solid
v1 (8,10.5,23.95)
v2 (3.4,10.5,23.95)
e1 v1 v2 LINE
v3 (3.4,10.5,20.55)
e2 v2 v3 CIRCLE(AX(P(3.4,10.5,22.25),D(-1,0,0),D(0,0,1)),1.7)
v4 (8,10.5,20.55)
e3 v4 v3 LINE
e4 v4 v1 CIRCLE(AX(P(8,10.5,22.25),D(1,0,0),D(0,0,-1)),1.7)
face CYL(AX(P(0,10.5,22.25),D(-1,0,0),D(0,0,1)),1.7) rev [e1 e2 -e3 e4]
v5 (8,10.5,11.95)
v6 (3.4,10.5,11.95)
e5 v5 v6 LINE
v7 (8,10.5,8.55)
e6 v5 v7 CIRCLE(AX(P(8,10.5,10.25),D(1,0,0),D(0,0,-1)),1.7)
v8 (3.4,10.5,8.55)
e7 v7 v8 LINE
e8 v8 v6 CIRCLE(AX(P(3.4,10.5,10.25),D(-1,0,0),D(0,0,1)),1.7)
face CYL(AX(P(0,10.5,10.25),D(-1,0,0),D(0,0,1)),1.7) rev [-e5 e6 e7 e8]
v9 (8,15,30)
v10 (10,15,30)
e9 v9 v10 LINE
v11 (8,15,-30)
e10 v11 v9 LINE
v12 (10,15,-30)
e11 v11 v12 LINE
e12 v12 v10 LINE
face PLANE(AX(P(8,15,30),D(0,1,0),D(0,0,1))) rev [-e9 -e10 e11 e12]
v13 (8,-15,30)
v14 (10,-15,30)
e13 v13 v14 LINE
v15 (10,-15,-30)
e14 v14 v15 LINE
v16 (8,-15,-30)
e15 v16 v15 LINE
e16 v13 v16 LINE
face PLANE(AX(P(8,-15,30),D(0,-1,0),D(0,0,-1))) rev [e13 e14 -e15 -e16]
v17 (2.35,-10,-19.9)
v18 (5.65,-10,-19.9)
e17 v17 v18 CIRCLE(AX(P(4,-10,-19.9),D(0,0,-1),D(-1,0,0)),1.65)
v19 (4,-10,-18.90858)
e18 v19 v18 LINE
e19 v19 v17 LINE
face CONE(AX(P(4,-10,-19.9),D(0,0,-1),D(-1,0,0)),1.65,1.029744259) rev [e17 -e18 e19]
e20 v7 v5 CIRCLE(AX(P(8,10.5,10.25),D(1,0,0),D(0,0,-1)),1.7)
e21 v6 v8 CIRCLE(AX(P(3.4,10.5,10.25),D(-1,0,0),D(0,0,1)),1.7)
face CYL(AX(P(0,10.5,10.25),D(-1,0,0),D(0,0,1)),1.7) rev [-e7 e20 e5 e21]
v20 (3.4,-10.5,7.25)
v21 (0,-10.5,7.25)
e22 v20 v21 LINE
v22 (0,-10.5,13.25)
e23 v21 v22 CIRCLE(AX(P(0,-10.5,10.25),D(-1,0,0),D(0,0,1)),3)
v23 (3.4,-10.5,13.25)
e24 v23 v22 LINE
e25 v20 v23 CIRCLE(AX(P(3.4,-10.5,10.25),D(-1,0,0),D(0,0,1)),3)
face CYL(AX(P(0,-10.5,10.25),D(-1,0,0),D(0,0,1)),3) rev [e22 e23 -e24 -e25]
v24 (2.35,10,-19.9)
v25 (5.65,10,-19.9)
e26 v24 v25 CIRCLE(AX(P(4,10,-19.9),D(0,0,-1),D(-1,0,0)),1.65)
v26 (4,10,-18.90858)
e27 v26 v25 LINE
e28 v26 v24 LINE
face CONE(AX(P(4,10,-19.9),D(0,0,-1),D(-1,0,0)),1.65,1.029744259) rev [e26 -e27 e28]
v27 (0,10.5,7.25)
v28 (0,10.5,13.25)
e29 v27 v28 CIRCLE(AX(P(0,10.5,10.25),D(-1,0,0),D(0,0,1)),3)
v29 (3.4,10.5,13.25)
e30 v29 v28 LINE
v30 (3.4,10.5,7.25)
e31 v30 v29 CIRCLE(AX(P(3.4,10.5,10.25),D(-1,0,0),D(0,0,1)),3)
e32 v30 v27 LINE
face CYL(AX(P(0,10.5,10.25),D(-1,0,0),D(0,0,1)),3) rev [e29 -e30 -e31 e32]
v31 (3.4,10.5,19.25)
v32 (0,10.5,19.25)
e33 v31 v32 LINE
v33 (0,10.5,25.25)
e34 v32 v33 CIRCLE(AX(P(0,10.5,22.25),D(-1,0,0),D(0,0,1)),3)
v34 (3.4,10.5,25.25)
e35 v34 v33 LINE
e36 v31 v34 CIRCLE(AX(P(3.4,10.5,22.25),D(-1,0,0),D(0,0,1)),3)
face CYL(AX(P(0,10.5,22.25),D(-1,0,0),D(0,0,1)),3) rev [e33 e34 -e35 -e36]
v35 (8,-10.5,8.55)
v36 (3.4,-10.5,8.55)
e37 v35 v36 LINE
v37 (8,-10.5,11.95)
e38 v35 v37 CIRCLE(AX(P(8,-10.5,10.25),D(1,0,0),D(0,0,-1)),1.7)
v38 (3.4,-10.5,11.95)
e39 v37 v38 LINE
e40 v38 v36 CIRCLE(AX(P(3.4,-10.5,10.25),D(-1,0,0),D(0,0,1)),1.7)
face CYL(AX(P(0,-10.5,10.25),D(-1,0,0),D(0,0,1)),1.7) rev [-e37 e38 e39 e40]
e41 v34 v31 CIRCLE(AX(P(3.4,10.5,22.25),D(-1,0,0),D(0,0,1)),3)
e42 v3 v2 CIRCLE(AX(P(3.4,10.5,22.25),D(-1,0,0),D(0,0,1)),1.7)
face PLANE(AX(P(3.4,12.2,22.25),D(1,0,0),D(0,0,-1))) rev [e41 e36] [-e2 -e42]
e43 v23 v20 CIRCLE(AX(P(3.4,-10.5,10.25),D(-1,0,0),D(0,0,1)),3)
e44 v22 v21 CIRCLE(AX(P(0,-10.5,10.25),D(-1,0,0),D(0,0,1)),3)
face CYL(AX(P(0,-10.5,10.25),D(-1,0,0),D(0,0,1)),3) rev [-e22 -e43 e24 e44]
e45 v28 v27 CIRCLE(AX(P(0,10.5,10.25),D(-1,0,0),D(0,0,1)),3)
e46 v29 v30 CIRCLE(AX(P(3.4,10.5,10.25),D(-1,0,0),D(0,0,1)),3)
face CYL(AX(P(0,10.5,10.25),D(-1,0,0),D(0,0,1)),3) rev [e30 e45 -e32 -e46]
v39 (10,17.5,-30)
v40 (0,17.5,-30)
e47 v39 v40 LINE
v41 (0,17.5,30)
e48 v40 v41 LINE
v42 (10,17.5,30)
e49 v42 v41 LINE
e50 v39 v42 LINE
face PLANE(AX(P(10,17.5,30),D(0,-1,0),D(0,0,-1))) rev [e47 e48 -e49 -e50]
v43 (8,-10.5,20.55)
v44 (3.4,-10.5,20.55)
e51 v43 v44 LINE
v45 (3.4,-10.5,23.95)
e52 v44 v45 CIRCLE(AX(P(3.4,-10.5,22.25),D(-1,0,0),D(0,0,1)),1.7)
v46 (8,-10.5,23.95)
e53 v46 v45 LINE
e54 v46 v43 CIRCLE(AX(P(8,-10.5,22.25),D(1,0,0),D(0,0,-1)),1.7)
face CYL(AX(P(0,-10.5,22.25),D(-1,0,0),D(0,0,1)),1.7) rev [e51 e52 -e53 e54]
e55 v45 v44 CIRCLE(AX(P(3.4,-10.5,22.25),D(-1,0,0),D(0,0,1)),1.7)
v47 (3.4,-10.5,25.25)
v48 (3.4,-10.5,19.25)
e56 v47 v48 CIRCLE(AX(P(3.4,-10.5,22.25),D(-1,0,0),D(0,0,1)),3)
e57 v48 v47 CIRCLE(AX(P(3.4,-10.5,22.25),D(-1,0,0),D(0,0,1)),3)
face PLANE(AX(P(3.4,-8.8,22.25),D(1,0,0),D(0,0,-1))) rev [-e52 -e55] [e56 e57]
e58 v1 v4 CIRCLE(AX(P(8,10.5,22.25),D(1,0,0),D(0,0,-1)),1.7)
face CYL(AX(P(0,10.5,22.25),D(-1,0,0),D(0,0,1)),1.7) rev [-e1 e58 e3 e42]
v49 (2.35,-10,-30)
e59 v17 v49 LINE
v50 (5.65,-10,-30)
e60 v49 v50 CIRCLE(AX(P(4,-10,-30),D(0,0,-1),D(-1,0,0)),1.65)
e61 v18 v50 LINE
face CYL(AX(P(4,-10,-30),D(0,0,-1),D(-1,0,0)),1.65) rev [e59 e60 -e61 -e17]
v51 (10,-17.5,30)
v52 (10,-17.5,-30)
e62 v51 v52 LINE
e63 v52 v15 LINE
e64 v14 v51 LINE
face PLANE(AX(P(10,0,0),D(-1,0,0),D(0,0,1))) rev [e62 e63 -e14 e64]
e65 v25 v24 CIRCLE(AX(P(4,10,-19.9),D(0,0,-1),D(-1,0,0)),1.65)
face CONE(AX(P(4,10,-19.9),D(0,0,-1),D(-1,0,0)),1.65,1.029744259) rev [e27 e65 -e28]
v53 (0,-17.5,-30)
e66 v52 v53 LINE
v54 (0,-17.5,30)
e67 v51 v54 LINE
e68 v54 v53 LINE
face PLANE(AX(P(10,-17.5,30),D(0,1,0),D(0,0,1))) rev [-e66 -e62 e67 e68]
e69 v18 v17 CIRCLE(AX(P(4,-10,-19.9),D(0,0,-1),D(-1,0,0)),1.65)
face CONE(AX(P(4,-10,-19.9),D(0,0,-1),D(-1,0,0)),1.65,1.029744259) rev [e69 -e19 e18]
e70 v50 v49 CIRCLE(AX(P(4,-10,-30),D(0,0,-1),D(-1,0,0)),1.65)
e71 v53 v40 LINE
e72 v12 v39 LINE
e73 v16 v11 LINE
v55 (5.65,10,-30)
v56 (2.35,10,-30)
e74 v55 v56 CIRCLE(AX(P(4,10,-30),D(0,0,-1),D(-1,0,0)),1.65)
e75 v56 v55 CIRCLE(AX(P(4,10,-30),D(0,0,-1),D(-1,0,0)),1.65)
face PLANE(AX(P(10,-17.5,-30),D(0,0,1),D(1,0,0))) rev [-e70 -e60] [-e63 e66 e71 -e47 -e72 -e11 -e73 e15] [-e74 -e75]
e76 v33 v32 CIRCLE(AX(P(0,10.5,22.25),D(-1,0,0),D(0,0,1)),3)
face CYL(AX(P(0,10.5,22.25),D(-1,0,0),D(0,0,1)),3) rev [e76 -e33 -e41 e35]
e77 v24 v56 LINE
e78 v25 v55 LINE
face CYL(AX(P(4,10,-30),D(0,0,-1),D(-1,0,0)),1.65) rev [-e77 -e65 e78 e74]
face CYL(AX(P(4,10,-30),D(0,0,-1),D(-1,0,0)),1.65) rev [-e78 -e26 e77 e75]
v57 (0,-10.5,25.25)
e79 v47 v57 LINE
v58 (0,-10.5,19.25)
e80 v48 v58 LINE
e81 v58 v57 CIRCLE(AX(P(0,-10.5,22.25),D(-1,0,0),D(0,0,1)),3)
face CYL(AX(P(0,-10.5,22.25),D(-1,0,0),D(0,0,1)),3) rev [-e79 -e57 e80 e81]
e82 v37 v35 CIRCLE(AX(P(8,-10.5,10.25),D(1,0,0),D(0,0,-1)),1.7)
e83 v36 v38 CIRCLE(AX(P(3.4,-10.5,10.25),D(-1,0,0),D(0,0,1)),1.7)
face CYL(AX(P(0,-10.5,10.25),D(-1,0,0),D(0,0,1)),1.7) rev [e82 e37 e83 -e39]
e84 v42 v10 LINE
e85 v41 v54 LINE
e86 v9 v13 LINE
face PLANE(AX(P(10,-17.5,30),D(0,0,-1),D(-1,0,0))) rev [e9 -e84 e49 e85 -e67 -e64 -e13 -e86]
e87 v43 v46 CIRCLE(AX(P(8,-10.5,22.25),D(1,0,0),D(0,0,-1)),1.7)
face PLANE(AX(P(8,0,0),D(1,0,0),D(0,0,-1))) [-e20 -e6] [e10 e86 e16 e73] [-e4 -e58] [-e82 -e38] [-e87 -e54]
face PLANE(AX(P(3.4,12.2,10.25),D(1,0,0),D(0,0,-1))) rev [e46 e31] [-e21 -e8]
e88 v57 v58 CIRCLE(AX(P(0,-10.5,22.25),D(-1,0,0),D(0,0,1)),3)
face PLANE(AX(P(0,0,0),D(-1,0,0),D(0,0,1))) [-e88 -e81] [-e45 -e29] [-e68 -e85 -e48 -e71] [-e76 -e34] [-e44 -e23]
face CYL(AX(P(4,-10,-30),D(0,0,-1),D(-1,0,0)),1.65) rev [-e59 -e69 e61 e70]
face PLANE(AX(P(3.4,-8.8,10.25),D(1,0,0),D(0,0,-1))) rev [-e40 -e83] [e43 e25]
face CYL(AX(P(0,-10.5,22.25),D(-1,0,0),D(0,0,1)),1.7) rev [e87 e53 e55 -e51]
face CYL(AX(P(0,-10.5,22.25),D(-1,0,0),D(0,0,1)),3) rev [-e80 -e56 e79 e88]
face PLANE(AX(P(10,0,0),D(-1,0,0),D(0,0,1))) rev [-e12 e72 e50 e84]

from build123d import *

# Parameters (mm, degrees)
SKETCH1_W                                            = 60
SKETCH1_H                                            = 35
BOSS_EXTRUDE1_DEPTH                                  = 10
SKETCH2_W                                            = 60
SKETCH2_H                                            = 30
CUT_EXTRUDE1_DEPTH                                   = 2
CBORE_FOR_M3_HEXAGON_SOCKET_HEAD_CAP_SCR_D           = 3.4
CBORE_FOR_M3_HEXAGON_SOCKET_HEAD_CAP_SCR_CBORE_D     = 6
CBORE_FOR_M3_HEXAGON_SOCKET_HEAD_CAP_SCR_CBORE_DEPTH = 3.4
M4_TAPPED_HOLE1_D                                    = 3.3
M4_TAPPED_HOLE1_DEPTH                                = 10.1
M4_TAPPED_HOLE1_TIP                                  = 0.991420021


with BuildPart() as part:
    # Sketch1 → Boss-Extrude1 (new body)
    with BuildSketch(Plane(origin=(0, 0, 0), x_dir=(0, 0, -1), z_dir=(1, 0, 0))):
        Rectangle(SKETCH1_W, SKETCH1_H)
    extrude(amount=BOSS_EXTRUDE1_DEPTH)

    # Sketch2 → Cut-Extrude1 (cut)
    with BuildSketch(Plane(origin=(10, 0, 0), x_dir=(0, 0, -1), z_dir=(1, 0, 0))):
        Rectangle(SKETCH2_W, SKETCH2_H)
    extrude(amount=-CUT_EXTRUDE1_DEPTH, mode=Mode.SUBTRACT)

    # CBORE for M3 Hexagon socket head cap screws1 (through all)
    with Locations(Plane.ZY):
        with Locations((22.25, 10.5), (10.25, 10.5), (10.25, -10.5), (22.25, -10.5)):
            CounterBoreHole(CBORE_FOR_M3_HEXAGON_SOCKET_HEAD_CAP_SCR_D / 2, CBORE_FOR_M3_HEXAGON_SOCKET_HEAD_CAP_SCR_CBORE_D / 2, CBORE_FOR_M3_HEXAGON_SOCKET_HEAD_CAP_SCR_CBORE_DEPTH)

    # M4 Tapped Hole1
    with Locations(Plane(origin=(0, 0, -30), x_dir=(-1, 0, 0), z_dir=(0, 0, -1))):
        with Locations((-4, -10), (-4, 10)):
            Hole(M4_TAPPED_HOLE1_D / 2, depth=M4_TAPPED_HOLE1_DEPTH)
            with Locations((0, 0, -(M4_TAPPED_HOLE1_DEPTH + M4_TAPPED_HOLE1_TIP / 2))):  # 118° drill point
                Cone(0, M4_TAPPED_HOLE1_D / 2, M4_TAPPED_HOLE1_TIP, mode=Mode.SUBTRACT)


solid = part.part
